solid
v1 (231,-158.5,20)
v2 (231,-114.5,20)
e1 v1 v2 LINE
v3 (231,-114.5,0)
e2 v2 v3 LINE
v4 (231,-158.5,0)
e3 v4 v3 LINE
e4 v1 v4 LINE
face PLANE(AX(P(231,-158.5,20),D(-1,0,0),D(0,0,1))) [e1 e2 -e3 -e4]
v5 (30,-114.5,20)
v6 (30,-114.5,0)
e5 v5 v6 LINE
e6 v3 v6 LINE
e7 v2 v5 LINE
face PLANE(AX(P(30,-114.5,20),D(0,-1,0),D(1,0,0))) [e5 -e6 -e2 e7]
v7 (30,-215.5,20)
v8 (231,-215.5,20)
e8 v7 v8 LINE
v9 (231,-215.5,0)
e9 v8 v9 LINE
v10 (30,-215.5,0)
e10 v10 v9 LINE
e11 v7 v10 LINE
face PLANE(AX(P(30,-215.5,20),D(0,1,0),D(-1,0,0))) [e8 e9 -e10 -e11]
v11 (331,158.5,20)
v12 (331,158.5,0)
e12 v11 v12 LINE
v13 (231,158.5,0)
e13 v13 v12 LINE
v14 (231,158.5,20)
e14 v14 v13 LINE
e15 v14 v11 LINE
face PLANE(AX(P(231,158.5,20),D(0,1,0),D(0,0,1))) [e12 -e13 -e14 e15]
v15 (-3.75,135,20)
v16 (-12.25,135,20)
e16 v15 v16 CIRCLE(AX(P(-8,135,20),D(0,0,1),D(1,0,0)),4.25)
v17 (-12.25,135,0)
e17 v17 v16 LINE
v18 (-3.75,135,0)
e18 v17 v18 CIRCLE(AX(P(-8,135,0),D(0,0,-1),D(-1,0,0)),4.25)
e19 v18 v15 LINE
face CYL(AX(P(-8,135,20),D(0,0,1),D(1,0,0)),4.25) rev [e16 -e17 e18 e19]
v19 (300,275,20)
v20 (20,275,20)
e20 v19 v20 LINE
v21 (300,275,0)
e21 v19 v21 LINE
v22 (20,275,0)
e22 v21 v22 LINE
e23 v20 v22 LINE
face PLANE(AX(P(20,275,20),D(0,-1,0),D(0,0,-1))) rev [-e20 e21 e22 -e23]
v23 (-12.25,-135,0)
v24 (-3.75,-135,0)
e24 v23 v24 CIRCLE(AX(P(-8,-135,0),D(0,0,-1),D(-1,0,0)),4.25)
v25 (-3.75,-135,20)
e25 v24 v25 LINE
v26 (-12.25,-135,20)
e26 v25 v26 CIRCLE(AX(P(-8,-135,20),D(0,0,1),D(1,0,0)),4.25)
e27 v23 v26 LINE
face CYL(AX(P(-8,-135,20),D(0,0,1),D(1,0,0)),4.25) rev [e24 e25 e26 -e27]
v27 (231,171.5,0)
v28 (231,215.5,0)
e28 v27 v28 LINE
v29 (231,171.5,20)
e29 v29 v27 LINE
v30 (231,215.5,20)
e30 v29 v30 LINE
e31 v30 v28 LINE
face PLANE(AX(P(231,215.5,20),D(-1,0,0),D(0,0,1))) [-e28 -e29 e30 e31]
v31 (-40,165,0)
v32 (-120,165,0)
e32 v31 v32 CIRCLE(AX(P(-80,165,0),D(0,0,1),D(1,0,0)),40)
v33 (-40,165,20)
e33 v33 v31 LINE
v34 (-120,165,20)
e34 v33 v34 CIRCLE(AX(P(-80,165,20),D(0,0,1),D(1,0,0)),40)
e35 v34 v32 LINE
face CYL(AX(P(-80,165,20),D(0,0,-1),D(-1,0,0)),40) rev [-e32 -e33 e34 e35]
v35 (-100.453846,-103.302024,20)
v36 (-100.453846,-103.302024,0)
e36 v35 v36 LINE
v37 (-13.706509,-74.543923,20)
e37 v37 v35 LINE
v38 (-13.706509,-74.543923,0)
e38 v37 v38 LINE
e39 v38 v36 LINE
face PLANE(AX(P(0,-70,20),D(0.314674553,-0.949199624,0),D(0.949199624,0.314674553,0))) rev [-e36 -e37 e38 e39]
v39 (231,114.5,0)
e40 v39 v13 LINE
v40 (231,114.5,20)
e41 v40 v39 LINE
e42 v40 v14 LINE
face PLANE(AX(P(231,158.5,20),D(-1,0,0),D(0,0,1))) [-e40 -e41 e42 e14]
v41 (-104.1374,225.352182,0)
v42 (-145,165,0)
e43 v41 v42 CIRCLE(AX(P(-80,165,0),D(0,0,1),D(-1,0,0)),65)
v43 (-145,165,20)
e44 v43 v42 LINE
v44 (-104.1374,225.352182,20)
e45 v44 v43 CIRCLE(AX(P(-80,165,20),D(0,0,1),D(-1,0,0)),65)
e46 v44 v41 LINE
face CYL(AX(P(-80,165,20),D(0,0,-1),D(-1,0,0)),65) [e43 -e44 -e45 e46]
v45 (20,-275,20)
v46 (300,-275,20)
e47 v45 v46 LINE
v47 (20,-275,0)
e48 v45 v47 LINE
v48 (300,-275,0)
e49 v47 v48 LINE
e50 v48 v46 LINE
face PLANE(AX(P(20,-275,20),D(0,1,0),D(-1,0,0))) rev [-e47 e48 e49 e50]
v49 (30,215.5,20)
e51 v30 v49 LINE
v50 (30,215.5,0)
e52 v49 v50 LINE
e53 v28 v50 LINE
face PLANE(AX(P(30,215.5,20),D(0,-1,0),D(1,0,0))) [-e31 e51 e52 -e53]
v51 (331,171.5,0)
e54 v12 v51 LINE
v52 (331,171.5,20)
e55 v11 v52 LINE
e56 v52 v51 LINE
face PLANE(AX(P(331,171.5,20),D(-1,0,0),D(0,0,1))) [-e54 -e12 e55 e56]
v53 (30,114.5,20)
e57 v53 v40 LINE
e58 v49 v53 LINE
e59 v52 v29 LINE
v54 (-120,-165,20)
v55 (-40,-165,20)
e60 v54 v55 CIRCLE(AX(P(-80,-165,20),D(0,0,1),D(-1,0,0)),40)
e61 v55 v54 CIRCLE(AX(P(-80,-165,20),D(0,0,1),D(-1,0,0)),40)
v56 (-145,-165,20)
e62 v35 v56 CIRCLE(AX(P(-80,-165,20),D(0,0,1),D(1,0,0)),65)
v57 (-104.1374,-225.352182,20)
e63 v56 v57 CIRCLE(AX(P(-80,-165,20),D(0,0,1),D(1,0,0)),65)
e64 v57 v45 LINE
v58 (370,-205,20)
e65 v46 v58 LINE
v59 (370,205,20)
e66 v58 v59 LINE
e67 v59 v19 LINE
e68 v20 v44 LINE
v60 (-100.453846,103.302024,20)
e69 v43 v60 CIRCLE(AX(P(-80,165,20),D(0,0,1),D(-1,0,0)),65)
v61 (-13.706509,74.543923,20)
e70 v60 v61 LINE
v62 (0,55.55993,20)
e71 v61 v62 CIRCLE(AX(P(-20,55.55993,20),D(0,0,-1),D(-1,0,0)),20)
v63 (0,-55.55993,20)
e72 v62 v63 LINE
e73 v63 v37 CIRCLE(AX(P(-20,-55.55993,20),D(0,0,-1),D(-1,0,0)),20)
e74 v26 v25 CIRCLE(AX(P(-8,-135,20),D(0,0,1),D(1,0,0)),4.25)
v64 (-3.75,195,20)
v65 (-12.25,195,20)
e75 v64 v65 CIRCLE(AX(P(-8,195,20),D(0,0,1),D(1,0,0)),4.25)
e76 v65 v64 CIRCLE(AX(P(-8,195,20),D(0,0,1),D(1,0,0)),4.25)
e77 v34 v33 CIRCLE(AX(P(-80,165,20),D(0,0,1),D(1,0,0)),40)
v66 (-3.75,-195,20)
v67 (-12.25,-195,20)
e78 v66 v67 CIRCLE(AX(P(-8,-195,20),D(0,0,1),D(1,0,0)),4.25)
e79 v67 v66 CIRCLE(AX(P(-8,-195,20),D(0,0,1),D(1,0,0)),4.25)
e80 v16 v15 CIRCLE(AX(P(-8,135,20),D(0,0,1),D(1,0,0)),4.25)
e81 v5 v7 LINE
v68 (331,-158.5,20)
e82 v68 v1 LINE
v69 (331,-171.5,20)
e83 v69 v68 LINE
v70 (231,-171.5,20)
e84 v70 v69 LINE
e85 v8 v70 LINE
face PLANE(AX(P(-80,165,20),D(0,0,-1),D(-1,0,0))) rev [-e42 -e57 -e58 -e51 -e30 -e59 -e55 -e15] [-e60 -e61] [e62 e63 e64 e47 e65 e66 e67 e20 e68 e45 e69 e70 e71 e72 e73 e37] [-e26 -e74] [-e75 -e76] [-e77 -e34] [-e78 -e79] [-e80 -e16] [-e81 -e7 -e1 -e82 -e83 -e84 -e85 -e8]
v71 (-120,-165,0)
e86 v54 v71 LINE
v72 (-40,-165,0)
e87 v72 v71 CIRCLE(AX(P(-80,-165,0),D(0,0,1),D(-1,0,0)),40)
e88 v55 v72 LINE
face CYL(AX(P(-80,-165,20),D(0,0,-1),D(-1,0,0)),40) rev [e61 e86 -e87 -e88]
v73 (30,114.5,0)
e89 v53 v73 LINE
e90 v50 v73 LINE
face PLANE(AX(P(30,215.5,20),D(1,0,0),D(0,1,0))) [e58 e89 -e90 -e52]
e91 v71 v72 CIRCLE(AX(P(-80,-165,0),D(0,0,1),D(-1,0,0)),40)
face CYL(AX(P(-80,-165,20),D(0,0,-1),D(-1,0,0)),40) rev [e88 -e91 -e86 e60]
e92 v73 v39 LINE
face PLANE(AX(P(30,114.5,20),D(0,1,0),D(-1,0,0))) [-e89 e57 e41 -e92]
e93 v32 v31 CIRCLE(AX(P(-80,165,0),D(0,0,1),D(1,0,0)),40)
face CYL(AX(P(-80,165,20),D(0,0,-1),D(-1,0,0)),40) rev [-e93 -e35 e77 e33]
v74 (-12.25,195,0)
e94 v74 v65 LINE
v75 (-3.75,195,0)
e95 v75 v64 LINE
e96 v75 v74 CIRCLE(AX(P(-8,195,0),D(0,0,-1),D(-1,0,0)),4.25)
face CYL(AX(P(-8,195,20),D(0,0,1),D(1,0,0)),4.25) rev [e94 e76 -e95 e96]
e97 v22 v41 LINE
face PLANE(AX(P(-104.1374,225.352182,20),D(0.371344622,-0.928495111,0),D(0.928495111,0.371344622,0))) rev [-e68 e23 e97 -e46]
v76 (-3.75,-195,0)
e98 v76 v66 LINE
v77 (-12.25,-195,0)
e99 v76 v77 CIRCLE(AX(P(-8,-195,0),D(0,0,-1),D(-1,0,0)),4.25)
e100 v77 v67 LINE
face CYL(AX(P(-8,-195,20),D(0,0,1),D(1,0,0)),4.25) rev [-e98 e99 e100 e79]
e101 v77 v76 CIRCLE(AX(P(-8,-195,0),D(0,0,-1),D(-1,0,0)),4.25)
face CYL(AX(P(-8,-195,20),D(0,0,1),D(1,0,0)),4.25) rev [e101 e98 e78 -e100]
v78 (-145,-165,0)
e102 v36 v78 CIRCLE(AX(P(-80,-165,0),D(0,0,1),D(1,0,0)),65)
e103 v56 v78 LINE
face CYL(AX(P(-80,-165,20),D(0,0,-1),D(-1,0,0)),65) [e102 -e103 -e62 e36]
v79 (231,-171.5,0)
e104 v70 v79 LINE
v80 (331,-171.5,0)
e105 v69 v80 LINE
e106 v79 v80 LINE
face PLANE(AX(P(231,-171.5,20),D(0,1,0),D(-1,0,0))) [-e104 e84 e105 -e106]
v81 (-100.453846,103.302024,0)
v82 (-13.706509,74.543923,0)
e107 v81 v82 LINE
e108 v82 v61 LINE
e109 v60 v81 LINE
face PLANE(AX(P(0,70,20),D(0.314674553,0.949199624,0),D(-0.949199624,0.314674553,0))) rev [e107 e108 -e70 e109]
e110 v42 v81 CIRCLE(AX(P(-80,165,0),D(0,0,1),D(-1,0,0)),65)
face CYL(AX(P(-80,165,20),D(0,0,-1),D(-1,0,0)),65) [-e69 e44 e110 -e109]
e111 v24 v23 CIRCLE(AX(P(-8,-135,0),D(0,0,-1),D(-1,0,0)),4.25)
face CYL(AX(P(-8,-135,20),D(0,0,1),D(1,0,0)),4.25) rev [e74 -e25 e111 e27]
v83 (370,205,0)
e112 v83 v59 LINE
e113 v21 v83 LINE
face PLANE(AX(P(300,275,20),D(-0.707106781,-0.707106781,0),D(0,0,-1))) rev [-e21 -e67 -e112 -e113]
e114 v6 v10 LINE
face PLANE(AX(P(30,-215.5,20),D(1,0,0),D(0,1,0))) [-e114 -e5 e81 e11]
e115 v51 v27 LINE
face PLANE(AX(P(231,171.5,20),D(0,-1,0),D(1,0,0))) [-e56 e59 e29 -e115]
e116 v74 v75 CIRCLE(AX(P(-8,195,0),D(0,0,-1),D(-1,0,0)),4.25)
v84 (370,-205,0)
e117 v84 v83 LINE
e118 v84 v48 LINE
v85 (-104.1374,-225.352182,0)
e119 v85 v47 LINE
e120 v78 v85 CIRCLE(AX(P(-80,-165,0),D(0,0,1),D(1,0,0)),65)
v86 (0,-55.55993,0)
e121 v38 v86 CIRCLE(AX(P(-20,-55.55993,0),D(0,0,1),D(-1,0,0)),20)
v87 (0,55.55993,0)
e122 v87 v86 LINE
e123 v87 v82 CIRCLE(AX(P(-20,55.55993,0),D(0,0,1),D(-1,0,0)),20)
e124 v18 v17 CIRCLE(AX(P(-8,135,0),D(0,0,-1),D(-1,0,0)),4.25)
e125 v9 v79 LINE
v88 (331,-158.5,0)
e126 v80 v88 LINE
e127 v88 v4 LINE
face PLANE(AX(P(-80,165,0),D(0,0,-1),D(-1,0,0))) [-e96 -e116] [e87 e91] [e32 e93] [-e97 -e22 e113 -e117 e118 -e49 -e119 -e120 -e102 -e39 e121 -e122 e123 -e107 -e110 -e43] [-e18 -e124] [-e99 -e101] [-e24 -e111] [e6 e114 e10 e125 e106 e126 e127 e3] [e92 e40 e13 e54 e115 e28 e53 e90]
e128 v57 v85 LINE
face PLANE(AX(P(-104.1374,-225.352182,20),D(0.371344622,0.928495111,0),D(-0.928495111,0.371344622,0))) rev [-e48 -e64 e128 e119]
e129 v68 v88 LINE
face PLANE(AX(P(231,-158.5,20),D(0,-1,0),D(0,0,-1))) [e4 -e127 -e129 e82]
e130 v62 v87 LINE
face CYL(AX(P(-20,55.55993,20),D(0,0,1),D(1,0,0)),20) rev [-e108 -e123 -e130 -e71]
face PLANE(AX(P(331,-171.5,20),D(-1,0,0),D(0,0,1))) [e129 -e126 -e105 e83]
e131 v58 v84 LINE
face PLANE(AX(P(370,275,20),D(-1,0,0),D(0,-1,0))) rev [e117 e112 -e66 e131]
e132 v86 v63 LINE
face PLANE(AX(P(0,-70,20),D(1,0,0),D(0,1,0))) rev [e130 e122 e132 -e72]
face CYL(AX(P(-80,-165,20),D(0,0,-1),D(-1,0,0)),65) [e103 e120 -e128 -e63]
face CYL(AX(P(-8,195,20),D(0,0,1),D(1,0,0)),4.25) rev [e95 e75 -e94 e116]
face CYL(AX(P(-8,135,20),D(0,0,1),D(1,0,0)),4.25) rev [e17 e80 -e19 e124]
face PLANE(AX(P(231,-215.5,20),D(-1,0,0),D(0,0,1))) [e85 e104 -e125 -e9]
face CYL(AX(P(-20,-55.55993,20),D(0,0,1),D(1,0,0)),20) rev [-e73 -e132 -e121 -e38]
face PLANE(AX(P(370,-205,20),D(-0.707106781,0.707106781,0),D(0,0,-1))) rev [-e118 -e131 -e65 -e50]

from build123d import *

# Parameters (mm, degrees)
SKETCH1_R           = 40
BOSS_EXTRUDE1_DEPTH = 20
M10_TAPPED_HOLE1_D  = 8.5
CHAMFER1_SIZE       = 70
FILLET1_R           = 20


with BuildPart() as part:
    # Sketch1 → Boss-Extrude1 (new body)
    with BuildSketch(Plane.XY):
        with BuildLine():
            Line((0, -70), (0, 70))
            Line((0, 70), (-100.453845954, 103.30202446))
            ThreePointArc((-100.453845954, 103.30202446), (-144.970416858, 163.039149842), (-104.13740045, 225.352182227))
            Line((-104.13740045, 225.352182227), (20, 275))
            Line((20, 275), (370, 275))
            Line((370, 275), (370, -275))
            Line((370, -275), (20, -275))
            Line((20, -275), (-104.13740045, -225.352182227))
            ThreePointArc((-104.13740045, -225.352182227), (-144.970416858, -163.039149842), (-100.453845954, -103.30202446))
            Line((-100.453845954, -103.30202446), (0, -70))
        make_face()
        with Locations((-80, 165)):
            Circle(SKETCH1_R, mode=Mode.SUBTRACT)
        with Locations(Location((-80, -165, 0), (0, 0, 180))):
            Circle(SKETCH1_R, mode=Mode.SUBTRACT)
        Polygon((231, 158.5), (231, 114.5), (30, 114.5), (30, 215.5), (231, 215.5), (231, 171.5), (331, 171.5), (331, 158.5), align=None, mode=Mode.SUBTRACT)
        Polygon((331, -171.5), (331, -158.5), (231, -158.5), (231, -114.5), (30, -114.5), (30, -215.5), (231, -215.5), (231, -171.5), align=None, mode=Mode.SUBTRACT)
    extrude(amount=BOSS_EXTRUDE1_DEPTH)

    # M10 Tapped Hole1 (through all)
    with Locations(Plane.XY.offset(20)):
        with Locations((-8, 195), (-8, 135), (-8, -135), (-8, -195)):
            Hole(M10_TAPPED_HOLE1_D / 2)

    # Chamfer1
    chamfer1_edges = [part.edges().sort_by_distance(p)[0] for p in [
        (370, 275, 10),
        (370, -275, 10),
    ]]
    chamfer(chamfer1_edges, length=CHAMFER1_SIZE)

    # Fillet1
    fillet1_edges = [part.edges().sort_by_distance(p)[0] for p in [
        (0, -70, 10),
        (0, 70, 10),
    ]]
    fillet(fillet1_edges, radius=FILLET1_R)


solid = part.part
